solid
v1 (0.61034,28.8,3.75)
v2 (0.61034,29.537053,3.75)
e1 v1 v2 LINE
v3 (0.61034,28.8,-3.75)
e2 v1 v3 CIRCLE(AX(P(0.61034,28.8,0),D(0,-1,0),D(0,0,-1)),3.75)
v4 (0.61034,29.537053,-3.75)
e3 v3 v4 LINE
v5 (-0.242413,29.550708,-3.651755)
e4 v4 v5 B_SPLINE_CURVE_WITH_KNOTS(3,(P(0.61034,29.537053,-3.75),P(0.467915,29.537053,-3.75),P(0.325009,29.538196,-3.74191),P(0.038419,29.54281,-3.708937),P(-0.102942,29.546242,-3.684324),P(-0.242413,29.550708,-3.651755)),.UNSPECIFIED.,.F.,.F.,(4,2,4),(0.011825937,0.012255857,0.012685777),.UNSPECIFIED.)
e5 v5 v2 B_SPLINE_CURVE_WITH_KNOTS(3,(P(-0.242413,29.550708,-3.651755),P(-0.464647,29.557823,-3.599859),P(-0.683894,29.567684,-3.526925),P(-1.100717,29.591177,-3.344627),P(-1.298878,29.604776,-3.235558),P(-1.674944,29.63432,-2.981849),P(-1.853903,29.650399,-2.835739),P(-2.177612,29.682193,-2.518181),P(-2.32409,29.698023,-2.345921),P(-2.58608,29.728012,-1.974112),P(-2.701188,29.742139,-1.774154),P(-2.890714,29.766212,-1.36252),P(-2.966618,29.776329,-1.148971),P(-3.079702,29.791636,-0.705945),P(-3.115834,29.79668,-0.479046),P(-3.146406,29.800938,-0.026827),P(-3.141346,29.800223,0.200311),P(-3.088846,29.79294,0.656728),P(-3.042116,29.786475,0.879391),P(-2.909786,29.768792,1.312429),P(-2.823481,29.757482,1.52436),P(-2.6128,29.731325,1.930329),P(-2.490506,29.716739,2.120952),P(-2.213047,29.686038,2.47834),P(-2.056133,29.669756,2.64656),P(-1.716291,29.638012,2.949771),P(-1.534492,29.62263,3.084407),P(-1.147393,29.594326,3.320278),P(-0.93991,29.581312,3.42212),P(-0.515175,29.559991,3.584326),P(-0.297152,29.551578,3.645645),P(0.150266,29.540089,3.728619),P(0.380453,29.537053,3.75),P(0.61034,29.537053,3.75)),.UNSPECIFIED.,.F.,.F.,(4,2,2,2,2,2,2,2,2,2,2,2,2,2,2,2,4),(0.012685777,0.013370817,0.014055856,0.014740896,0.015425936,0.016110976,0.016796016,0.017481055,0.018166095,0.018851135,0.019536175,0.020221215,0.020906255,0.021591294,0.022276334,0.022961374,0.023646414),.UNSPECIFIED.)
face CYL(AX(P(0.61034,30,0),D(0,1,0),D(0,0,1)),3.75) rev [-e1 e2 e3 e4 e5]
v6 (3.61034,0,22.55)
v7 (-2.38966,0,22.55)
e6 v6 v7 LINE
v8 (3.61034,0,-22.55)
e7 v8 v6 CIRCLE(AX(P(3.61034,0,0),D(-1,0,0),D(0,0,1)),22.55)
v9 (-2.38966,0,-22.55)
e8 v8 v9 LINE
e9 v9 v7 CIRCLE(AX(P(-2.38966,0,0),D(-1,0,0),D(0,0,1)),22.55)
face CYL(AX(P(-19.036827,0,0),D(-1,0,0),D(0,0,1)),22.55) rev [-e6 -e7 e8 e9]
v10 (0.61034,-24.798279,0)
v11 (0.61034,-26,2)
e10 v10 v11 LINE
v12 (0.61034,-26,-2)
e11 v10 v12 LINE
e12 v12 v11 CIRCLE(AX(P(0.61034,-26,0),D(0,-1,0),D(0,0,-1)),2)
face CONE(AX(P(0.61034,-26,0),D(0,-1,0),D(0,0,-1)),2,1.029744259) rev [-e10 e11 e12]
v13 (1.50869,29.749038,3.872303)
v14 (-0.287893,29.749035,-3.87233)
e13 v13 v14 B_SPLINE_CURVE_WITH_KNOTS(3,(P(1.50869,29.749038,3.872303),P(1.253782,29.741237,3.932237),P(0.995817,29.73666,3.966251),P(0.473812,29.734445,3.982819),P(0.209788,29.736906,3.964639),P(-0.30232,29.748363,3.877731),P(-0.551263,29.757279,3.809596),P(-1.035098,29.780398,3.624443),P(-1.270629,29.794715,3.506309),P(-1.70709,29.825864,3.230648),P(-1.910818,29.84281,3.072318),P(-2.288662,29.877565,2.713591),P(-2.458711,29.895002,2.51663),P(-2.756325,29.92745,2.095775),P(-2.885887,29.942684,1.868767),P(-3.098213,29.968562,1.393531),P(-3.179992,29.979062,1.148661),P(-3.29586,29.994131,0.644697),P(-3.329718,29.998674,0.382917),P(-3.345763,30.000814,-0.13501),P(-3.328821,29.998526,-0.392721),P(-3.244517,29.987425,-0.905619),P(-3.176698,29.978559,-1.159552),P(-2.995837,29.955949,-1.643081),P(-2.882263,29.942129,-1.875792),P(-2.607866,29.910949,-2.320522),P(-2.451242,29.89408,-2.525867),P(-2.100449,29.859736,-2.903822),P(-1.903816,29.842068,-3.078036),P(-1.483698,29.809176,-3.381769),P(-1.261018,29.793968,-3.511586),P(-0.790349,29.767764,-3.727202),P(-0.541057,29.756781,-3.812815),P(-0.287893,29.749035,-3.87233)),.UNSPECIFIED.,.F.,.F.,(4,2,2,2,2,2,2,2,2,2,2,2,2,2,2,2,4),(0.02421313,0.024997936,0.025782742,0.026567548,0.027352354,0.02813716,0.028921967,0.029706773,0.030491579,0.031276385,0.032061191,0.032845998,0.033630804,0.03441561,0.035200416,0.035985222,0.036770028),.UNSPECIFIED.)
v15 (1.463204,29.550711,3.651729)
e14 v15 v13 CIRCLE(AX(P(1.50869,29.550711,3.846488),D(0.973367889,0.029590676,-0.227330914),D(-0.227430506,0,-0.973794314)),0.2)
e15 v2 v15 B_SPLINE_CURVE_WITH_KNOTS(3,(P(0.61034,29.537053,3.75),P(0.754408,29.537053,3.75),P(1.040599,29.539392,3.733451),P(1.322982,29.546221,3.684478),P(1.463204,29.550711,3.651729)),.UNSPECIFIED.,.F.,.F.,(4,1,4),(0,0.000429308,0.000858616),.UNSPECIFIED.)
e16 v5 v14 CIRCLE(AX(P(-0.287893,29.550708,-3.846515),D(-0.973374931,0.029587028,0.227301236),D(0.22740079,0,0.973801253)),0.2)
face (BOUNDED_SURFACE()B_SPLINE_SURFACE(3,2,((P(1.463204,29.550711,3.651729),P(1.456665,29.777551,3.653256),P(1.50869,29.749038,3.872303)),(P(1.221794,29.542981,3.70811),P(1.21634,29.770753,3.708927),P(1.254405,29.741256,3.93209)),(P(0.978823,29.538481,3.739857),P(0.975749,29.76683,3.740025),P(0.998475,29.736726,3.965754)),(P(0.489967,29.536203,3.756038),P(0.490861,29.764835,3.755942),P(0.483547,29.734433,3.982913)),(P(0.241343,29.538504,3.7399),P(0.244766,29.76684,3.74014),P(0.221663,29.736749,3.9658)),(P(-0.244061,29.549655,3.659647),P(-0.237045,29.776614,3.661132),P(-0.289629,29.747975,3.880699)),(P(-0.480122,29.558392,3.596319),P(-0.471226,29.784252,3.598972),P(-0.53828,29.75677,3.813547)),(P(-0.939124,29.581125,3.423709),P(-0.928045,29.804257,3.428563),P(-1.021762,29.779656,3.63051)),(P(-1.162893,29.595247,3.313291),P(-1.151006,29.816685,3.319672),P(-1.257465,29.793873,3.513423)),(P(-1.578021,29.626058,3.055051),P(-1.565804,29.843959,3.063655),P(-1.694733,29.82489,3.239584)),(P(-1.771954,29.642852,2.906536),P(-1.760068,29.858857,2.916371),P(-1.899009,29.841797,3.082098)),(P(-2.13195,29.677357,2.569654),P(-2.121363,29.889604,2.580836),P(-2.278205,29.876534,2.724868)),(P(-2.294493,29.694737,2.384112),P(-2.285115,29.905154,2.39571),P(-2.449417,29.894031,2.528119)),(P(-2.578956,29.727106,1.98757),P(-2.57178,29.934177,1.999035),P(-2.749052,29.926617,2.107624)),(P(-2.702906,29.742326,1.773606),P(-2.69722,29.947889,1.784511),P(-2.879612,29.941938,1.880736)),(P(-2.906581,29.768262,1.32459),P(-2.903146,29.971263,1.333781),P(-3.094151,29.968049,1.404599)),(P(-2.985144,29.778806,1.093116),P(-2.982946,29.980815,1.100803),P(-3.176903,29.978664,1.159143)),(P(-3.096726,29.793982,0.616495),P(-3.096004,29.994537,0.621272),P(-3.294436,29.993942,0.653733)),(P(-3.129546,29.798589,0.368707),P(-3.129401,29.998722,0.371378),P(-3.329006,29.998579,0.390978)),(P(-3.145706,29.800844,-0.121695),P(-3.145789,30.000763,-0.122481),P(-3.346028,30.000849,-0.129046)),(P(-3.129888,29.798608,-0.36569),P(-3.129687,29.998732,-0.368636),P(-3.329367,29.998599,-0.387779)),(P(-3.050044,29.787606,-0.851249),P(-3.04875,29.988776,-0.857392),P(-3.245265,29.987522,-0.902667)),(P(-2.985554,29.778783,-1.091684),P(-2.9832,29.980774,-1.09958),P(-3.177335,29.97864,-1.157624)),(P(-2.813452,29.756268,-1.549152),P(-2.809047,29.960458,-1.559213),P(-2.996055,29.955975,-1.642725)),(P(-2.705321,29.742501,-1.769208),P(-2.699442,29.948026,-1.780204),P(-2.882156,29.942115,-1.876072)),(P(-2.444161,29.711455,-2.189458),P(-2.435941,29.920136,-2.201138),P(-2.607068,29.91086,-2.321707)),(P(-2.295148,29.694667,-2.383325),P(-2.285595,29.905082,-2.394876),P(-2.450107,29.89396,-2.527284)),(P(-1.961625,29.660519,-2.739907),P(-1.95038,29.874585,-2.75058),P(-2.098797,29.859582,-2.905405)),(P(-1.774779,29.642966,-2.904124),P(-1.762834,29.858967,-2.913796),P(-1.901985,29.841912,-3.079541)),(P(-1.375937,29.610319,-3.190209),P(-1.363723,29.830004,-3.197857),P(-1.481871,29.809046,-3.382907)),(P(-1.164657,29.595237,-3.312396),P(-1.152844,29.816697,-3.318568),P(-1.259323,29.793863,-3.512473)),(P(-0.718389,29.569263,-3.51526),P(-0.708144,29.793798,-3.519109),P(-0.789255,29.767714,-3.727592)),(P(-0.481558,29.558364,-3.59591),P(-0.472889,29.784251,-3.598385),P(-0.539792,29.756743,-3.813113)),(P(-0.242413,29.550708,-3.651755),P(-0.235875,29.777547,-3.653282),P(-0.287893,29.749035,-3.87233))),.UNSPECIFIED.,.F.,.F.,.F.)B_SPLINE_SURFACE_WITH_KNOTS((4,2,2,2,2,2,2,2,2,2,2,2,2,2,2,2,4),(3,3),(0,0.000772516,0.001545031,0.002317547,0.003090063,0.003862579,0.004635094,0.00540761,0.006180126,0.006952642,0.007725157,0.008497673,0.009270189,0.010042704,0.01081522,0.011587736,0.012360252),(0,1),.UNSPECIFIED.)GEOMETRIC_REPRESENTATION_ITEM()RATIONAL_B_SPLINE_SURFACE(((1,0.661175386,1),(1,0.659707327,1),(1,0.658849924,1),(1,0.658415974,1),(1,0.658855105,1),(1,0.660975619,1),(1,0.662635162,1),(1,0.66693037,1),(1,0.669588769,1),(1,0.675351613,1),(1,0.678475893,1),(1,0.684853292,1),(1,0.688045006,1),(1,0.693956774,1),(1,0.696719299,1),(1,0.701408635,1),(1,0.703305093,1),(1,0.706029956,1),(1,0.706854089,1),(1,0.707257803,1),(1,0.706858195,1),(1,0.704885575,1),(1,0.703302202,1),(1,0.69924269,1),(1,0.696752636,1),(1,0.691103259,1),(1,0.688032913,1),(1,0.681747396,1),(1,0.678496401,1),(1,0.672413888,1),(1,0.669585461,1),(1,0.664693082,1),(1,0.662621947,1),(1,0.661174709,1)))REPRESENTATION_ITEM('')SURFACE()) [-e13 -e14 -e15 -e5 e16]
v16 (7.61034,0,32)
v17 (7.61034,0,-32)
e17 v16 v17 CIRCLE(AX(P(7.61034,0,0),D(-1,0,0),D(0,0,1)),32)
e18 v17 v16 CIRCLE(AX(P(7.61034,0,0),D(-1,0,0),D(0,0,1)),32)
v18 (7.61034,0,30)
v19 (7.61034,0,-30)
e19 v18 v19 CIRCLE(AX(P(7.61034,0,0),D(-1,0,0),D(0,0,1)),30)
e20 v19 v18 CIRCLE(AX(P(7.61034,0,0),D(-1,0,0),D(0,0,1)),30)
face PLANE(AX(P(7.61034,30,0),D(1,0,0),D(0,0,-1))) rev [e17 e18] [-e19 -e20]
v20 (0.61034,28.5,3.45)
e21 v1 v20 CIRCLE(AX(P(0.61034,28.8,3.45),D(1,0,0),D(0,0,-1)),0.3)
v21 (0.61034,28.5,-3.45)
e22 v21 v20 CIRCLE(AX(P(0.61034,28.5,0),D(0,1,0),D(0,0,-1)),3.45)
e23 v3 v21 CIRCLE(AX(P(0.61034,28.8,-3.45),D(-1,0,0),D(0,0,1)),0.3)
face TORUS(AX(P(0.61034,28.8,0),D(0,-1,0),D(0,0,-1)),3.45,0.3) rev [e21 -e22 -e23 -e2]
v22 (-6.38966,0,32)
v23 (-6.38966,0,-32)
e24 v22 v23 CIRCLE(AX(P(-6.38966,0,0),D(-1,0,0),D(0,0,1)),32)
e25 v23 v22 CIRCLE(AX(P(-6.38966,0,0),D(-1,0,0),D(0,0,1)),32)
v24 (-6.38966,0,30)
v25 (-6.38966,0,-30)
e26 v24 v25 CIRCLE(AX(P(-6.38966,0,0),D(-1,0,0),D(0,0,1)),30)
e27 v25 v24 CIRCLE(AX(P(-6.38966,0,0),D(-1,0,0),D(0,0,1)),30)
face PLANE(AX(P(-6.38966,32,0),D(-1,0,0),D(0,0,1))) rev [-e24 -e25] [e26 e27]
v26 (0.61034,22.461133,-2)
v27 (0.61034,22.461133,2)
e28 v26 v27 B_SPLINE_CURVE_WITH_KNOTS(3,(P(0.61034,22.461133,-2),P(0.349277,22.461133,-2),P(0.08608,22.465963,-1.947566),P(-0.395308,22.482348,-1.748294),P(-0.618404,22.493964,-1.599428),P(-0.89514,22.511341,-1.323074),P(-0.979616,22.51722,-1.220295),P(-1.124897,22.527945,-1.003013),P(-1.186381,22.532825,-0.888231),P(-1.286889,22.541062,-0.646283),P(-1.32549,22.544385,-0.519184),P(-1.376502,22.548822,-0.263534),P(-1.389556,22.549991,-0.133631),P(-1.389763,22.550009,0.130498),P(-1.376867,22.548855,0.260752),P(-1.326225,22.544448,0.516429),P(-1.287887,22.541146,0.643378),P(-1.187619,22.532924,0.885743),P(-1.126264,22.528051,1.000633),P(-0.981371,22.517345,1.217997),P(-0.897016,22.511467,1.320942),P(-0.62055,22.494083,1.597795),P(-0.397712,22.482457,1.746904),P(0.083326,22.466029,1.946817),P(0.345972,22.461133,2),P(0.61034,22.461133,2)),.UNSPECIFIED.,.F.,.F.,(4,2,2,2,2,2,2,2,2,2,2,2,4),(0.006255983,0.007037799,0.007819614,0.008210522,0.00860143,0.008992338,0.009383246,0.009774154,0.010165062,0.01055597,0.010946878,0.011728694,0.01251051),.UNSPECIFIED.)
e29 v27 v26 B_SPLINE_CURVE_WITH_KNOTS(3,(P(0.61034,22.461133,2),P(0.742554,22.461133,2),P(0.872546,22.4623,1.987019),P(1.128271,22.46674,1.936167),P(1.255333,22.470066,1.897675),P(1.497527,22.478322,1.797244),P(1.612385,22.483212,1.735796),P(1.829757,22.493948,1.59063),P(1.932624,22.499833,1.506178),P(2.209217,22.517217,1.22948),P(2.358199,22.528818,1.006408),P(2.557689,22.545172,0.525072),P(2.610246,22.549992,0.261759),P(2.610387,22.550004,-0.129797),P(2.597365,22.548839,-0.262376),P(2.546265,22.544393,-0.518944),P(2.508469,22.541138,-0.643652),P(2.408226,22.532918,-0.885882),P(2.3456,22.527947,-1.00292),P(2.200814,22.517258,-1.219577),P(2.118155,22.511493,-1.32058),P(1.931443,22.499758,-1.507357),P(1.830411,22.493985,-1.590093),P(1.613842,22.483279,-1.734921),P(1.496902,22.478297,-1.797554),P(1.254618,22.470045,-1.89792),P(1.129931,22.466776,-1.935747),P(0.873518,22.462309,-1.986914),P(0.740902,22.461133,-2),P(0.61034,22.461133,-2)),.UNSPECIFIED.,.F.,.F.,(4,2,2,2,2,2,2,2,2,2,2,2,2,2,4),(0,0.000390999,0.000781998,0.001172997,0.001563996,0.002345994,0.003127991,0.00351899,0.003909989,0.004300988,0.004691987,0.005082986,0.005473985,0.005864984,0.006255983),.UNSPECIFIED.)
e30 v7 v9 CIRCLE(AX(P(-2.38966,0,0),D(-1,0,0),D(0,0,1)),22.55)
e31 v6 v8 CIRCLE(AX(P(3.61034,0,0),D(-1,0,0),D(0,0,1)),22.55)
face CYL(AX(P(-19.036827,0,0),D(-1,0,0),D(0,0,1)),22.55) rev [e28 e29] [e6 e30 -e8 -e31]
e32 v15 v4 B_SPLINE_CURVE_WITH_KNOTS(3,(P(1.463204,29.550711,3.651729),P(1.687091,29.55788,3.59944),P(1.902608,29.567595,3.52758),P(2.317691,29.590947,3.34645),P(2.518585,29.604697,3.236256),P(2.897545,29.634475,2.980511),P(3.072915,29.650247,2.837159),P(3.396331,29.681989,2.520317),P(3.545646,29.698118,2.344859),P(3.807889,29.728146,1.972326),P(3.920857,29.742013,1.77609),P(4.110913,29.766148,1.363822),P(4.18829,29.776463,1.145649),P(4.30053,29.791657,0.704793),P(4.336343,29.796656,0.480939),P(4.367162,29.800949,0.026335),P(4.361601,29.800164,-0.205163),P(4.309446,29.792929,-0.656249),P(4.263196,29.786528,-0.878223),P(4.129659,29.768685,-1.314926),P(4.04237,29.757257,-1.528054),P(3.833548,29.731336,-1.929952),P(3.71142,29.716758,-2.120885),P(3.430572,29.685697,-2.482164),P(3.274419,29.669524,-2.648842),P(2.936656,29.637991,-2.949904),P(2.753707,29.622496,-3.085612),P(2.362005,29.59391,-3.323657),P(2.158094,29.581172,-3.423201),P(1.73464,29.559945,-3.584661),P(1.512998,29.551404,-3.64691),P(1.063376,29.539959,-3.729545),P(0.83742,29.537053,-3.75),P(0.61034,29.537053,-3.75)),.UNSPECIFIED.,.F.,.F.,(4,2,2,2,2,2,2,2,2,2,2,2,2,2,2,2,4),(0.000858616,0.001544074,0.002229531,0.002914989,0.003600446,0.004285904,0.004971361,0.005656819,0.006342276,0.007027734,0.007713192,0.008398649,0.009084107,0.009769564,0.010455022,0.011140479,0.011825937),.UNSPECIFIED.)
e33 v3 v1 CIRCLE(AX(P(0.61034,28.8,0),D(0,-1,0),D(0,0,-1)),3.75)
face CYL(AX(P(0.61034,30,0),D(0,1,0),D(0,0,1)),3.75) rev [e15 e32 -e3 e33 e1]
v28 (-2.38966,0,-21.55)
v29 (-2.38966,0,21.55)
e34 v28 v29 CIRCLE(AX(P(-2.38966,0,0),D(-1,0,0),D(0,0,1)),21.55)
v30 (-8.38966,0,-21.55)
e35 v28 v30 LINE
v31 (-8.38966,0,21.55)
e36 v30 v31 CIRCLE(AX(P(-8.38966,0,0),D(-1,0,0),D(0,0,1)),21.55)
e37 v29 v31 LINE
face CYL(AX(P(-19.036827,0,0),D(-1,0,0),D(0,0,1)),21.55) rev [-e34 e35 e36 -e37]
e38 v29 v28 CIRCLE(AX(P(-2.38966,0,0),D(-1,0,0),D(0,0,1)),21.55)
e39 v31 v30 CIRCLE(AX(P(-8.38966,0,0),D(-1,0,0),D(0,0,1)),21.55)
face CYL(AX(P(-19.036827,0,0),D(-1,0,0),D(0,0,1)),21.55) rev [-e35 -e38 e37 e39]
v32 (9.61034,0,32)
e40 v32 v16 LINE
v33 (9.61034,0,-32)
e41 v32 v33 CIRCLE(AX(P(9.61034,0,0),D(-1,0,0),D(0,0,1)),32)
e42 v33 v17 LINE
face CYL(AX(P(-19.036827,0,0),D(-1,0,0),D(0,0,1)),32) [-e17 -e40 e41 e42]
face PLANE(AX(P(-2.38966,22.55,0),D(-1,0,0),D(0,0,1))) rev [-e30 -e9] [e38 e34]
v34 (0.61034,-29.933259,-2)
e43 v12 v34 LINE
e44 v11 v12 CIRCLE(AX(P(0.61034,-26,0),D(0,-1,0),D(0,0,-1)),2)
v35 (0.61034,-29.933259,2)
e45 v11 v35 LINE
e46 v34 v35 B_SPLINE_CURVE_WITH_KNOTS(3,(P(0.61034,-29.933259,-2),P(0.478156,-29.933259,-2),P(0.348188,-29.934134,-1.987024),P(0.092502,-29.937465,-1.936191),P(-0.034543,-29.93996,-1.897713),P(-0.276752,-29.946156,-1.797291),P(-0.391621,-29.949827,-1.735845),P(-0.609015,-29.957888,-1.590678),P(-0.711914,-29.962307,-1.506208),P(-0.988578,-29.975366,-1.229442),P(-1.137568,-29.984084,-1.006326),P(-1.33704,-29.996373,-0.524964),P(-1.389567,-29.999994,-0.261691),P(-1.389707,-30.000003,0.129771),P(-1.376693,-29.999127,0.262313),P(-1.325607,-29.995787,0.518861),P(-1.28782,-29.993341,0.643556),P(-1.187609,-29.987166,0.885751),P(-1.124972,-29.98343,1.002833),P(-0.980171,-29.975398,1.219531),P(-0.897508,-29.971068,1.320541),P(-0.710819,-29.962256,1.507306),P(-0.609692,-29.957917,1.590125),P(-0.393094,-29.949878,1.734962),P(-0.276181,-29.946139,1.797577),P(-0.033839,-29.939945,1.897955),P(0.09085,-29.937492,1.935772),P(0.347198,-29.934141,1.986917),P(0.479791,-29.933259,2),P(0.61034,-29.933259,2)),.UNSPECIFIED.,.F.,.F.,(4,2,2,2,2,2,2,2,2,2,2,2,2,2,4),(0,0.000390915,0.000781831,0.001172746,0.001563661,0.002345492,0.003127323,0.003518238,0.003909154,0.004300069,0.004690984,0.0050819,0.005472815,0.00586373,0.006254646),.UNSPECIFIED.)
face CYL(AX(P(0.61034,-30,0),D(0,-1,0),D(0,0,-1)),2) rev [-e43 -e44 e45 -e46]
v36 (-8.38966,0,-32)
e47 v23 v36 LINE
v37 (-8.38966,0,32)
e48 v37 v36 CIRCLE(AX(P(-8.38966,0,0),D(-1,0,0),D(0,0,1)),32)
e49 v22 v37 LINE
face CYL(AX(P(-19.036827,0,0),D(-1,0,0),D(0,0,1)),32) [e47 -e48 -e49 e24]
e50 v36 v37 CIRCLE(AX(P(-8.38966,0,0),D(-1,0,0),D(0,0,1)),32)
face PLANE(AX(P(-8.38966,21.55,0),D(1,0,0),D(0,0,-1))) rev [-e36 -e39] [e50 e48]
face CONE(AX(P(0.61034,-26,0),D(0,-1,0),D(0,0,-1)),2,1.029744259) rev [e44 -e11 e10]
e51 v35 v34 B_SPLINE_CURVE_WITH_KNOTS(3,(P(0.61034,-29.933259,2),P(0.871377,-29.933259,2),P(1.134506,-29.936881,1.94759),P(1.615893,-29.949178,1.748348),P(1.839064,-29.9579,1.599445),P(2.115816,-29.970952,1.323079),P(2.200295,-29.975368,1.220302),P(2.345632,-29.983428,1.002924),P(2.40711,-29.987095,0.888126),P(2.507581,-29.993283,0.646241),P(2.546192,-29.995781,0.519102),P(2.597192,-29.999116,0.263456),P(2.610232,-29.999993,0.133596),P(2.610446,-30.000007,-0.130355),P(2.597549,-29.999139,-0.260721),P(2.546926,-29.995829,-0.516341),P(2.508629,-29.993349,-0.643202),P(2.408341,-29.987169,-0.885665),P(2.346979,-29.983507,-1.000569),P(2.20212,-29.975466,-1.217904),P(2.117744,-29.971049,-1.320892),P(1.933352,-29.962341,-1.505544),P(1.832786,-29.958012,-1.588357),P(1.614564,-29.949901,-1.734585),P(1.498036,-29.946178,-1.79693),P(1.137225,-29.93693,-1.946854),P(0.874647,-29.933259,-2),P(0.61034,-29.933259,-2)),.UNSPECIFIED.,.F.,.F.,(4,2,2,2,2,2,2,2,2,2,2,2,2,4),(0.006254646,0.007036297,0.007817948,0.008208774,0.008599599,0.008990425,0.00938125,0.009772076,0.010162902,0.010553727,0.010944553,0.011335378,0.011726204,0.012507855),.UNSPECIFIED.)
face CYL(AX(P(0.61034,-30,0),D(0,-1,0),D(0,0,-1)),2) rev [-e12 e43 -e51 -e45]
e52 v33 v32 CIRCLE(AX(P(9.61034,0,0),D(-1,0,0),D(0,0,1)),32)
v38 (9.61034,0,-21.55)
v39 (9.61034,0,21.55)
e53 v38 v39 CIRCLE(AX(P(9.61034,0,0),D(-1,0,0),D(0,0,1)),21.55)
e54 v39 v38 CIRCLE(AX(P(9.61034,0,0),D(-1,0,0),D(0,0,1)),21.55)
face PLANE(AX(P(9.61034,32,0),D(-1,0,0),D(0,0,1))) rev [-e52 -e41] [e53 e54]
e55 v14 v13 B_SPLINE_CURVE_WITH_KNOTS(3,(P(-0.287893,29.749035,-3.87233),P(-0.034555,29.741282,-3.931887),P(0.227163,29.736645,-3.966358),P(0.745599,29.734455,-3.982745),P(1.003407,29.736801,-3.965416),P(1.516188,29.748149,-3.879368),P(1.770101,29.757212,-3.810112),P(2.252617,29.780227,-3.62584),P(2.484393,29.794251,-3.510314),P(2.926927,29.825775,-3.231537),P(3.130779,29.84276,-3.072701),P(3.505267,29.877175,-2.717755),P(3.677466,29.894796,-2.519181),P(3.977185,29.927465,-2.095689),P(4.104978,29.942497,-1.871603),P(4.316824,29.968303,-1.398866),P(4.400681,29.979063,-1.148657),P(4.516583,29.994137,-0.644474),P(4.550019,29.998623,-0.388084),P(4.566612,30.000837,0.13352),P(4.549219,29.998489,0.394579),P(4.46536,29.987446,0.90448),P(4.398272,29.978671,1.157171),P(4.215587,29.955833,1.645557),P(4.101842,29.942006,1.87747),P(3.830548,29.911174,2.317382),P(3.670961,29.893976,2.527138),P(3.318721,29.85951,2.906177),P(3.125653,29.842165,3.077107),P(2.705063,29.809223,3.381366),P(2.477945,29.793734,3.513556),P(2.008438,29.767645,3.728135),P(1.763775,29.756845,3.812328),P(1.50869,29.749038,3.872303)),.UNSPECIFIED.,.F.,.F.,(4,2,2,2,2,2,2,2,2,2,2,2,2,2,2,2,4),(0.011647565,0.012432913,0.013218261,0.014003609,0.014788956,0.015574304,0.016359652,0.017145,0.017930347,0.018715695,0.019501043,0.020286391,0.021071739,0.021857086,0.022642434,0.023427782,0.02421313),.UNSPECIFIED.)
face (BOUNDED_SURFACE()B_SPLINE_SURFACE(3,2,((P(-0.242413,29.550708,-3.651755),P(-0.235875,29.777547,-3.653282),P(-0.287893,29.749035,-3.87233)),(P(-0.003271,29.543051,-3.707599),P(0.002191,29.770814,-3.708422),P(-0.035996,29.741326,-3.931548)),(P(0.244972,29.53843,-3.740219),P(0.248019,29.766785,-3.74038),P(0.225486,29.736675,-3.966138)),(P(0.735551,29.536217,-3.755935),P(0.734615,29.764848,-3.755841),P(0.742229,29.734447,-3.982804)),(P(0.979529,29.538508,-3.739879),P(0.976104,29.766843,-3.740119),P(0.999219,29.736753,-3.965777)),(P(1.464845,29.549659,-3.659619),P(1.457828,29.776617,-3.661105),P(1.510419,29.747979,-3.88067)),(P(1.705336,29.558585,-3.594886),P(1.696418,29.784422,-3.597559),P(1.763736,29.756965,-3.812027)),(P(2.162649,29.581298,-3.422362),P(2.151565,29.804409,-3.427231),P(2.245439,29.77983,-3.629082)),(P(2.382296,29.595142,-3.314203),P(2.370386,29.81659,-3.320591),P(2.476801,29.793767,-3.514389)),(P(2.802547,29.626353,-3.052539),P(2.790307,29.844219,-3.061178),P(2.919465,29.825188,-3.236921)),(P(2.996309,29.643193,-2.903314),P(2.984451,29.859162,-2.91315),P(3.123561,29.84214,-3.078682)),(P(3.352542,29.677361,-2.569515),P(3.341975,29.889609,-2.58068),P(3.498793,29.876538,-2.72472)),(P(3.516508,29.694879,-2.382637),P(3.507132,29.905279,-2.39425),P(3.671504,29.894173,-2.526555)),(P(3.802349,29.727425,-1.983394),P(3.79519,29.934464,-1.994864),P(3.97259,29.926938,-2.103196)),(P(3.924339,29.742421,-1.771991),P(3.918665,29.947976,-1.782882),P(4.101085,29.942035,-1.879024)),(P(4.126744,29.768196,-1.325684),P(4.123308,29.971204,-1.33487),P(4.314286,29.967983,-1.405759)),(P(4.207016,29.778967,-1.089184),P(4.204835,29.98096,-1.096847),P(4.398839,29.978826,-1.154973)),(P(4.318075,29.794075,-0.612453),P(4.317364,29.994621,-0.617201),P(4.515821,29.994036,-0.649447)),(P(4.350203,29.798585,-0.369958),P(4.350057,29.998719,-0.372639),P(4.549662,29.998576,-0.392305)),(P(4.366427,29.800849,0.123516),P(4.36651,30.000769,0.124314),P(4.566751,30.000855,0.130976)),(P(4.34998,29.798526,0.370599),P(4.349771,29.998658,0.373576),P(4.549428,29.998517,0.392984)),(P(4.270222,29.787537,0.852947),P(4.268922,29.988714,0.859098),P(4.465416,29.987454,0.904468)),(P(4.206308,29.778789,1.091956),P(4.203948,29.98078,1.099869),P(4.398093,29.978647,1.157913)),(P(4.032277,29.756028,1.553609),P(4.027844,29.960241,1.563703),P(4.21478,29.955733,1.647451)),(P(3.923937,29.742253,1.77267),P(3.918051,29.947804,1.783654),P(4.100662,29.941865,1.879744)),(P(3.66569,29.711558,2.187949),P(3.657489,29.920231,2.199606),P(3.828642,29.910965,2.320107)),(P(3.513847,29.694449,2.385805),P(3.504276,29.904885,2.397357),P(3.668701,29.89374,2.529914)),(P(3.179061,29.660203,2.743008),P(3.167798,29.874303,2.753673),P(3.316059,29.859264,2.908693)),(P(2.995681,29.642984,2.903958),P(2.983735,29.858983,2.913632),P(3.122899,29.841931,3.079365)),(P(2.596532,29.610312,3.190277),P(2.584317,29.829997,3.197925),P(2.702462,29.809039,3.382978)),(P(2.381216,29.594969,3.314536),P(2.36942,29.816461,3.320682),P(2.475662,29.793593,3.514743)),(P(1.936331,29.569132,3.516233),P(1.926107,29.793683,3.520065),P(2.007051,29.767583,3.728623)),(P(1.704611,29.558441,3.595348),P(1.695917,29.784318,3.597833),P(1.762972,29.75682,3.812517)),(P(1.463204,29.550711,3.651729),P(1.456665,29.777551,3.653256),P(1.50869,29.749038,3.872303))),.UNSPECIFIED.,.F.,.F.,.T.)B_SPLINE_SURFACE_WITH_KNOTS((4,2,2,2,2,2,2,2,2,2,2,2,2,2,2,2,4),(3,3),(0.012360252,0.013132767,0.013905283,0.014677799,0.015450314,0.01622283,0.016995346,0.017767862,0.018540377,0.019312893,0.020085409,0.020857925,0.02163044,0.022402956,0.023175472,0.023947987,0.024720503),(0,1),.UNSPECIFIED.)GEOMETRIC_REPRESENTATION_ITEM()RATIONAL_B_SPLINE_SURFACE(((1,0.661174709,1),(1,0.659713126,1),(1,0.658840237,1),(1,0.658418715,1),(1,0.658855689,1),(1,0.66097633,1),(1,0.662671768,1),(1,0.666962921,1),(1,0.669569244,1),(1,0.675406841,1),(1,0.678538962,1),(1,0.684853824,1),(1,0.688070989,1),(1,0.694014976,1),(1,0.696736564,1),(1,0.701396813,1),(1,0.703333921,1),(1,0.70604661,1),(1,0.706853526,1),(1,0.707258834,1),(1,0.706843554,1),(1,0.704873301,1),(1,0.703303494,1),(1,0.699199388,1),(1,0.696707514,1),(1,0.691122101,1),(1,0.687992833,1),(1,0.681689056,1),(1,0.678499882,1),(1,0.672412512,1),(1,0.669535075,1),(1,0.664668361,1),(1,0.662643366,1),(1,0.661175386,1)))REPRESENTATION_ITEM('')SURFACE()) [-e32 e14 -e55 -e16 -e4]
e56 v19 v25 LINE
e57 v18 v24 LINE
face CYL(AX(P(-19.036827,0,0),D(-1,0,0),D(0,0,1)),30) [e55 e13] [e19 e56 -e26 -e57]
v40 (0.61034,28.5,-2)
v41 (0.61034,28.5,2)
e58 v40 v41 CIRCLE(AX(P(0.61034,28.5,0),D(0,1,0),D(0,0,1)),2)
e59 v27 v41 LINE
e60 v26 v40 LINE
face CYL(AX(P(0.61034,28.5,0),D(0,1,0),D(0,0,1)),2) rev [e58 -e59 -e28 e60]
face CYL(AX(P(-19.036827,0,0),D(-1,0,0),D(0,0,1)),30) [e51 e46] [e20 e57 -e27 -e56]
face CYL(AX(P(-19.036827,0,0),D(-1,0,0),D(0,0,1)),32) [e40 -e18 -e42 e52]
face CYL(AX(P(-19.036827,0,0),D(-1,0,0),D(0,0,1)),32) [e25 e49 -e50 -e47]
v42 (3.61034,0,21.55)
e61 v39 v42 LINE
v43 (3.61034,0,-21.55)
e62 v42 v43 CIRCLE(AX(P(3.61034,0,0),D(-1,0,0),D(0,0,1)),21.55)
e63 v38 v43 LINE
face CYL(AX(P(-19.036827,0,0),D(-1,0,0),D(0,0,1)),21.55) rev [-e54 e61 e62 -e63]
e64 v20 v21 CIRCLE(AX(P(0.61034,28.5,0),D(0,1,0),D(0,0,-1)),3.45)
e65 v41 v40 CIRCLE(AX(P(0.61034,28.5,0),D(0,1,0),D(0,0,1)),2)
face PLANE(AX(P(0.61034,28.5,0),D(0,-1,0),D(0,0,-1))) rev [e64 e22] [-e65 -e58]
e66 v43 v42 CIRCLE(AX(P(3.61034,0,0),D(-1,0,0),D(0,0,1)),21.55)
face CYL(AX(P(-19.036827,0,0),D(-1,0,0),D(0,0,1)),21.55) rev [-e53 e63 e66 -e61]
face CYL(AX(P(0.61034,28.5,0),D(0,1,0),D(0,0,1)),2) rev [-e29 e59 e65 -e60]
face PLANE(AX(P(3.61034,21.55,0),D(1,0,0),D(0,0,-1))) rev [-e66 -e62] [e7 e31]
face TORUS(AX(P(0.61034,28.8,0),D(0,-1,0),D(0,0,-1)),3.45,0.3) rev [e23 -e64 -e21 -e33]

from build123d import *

# Parameters (mm, degrees)
HOLE1_D           = 7.5
HOLE1_DEPTH       = 1.5
HOLE2_REACH       = 71.113
HOLE2_BORE_R      = 2
DOWEL_HOLE1_D     = 4
DOWEL_HOLE1_DEPTH = 4
DOWEL_HOLE1_TIP   = 1.201721238
FILLET1_R         = 0.2
FILLET2_R         = 0.3


with BuildPart() as part:
    # Sketch1 → Revolve1 (revolve)
    with BuildSketch(Plane.XY, mode=Mode.PRIVATE) as revolve1_sk:
        Polygon((-8.389660143, 21.55), (-8.389660143, 32), (-6.389660143, 32), (-6.389660143, 30), (7.610339857, 30), (7.610339857, 32), (9.610339857, 32), (9.610339857, 21.55), (3.610339857, 21.55), (3.610339857, 22.55), (-2.389660143, 22.55), (-2.389660143, 21.55), align=None)
    revolve(revolve1_sk.sketch.rotate(Axis((-19.036826505, 0, 0), (1, 0, 0)), 90), axis=Axis((-19.036826505, 0, 0), (1, 0, 0)))

    # Hole1
    with Locations(Plane(origin=(0, 30, 0), x_dir=(1, 0, 0), z_dir=(0, 1, 0))):
        with Locations((0.610339857, 0)):
            Hole(HOLE1_D / 2, depth=HOLE1_DEPTH)

    # Hole2 bore → Hole2 (cut, up to next)
    with BuildSketch(Plane(origin=(0, 28.5, 0), x_dir=(1, 0, 0), z_dir=(0, 1, 0)), mode=Mode.PRIVATE) as hole2_sk1:
        with Locations((0.610339857, 0)):
            Circle(HOLE2_BORE_R)
    hole2_tool1 = extrude(hole2_sk1.sketch, amount=-HOLE2_REACH, mode=Mode.PRIVATE) & part.part
    add(hole2_tool1.solids().sort_by_distance((0.61034, 28.5, 0))[0], mode=Mode.SUBTRACT)

    # Dowel Hole1
    with Locations(Plane(origin=(0, -30, 0), x_dir=(-1, 0, 0), z_dir=(0, -1, 0))):
        with Locations((-0.610339857, 0)):
            Hole(DOWEL_HOLE1_D / 2, depth=DOWEL_HOLE1_DEPTH)
            with Locations((0, 0, -(DOWEL_HOLE1_DEPTH + DOWEL_HOLE1_TIP / 2))):  # 118° drill point
                Cone(0, DOWEL_HOLE1_D / 2, DOWEL_HOLE1_TIP, mode=Mode.SUBTRACT)

    # Fillet1
    fillet1_edges = [part.edges().sort_by_distance(p)[0] for p in [
        (4.360339864, 29.999999997, -1e-09),
    ]]
    fillet(fillet1_edges, radius=FILLET1_R)

    # Fillet2
    fillet2_edges = [part.edges().sort_by_distance(p)[0] for p in [
        (4.360339857, 28.5, 0),
    ]]
    fillet(fillet2_edges, radius=FILLET2_R)


solid = part.part
